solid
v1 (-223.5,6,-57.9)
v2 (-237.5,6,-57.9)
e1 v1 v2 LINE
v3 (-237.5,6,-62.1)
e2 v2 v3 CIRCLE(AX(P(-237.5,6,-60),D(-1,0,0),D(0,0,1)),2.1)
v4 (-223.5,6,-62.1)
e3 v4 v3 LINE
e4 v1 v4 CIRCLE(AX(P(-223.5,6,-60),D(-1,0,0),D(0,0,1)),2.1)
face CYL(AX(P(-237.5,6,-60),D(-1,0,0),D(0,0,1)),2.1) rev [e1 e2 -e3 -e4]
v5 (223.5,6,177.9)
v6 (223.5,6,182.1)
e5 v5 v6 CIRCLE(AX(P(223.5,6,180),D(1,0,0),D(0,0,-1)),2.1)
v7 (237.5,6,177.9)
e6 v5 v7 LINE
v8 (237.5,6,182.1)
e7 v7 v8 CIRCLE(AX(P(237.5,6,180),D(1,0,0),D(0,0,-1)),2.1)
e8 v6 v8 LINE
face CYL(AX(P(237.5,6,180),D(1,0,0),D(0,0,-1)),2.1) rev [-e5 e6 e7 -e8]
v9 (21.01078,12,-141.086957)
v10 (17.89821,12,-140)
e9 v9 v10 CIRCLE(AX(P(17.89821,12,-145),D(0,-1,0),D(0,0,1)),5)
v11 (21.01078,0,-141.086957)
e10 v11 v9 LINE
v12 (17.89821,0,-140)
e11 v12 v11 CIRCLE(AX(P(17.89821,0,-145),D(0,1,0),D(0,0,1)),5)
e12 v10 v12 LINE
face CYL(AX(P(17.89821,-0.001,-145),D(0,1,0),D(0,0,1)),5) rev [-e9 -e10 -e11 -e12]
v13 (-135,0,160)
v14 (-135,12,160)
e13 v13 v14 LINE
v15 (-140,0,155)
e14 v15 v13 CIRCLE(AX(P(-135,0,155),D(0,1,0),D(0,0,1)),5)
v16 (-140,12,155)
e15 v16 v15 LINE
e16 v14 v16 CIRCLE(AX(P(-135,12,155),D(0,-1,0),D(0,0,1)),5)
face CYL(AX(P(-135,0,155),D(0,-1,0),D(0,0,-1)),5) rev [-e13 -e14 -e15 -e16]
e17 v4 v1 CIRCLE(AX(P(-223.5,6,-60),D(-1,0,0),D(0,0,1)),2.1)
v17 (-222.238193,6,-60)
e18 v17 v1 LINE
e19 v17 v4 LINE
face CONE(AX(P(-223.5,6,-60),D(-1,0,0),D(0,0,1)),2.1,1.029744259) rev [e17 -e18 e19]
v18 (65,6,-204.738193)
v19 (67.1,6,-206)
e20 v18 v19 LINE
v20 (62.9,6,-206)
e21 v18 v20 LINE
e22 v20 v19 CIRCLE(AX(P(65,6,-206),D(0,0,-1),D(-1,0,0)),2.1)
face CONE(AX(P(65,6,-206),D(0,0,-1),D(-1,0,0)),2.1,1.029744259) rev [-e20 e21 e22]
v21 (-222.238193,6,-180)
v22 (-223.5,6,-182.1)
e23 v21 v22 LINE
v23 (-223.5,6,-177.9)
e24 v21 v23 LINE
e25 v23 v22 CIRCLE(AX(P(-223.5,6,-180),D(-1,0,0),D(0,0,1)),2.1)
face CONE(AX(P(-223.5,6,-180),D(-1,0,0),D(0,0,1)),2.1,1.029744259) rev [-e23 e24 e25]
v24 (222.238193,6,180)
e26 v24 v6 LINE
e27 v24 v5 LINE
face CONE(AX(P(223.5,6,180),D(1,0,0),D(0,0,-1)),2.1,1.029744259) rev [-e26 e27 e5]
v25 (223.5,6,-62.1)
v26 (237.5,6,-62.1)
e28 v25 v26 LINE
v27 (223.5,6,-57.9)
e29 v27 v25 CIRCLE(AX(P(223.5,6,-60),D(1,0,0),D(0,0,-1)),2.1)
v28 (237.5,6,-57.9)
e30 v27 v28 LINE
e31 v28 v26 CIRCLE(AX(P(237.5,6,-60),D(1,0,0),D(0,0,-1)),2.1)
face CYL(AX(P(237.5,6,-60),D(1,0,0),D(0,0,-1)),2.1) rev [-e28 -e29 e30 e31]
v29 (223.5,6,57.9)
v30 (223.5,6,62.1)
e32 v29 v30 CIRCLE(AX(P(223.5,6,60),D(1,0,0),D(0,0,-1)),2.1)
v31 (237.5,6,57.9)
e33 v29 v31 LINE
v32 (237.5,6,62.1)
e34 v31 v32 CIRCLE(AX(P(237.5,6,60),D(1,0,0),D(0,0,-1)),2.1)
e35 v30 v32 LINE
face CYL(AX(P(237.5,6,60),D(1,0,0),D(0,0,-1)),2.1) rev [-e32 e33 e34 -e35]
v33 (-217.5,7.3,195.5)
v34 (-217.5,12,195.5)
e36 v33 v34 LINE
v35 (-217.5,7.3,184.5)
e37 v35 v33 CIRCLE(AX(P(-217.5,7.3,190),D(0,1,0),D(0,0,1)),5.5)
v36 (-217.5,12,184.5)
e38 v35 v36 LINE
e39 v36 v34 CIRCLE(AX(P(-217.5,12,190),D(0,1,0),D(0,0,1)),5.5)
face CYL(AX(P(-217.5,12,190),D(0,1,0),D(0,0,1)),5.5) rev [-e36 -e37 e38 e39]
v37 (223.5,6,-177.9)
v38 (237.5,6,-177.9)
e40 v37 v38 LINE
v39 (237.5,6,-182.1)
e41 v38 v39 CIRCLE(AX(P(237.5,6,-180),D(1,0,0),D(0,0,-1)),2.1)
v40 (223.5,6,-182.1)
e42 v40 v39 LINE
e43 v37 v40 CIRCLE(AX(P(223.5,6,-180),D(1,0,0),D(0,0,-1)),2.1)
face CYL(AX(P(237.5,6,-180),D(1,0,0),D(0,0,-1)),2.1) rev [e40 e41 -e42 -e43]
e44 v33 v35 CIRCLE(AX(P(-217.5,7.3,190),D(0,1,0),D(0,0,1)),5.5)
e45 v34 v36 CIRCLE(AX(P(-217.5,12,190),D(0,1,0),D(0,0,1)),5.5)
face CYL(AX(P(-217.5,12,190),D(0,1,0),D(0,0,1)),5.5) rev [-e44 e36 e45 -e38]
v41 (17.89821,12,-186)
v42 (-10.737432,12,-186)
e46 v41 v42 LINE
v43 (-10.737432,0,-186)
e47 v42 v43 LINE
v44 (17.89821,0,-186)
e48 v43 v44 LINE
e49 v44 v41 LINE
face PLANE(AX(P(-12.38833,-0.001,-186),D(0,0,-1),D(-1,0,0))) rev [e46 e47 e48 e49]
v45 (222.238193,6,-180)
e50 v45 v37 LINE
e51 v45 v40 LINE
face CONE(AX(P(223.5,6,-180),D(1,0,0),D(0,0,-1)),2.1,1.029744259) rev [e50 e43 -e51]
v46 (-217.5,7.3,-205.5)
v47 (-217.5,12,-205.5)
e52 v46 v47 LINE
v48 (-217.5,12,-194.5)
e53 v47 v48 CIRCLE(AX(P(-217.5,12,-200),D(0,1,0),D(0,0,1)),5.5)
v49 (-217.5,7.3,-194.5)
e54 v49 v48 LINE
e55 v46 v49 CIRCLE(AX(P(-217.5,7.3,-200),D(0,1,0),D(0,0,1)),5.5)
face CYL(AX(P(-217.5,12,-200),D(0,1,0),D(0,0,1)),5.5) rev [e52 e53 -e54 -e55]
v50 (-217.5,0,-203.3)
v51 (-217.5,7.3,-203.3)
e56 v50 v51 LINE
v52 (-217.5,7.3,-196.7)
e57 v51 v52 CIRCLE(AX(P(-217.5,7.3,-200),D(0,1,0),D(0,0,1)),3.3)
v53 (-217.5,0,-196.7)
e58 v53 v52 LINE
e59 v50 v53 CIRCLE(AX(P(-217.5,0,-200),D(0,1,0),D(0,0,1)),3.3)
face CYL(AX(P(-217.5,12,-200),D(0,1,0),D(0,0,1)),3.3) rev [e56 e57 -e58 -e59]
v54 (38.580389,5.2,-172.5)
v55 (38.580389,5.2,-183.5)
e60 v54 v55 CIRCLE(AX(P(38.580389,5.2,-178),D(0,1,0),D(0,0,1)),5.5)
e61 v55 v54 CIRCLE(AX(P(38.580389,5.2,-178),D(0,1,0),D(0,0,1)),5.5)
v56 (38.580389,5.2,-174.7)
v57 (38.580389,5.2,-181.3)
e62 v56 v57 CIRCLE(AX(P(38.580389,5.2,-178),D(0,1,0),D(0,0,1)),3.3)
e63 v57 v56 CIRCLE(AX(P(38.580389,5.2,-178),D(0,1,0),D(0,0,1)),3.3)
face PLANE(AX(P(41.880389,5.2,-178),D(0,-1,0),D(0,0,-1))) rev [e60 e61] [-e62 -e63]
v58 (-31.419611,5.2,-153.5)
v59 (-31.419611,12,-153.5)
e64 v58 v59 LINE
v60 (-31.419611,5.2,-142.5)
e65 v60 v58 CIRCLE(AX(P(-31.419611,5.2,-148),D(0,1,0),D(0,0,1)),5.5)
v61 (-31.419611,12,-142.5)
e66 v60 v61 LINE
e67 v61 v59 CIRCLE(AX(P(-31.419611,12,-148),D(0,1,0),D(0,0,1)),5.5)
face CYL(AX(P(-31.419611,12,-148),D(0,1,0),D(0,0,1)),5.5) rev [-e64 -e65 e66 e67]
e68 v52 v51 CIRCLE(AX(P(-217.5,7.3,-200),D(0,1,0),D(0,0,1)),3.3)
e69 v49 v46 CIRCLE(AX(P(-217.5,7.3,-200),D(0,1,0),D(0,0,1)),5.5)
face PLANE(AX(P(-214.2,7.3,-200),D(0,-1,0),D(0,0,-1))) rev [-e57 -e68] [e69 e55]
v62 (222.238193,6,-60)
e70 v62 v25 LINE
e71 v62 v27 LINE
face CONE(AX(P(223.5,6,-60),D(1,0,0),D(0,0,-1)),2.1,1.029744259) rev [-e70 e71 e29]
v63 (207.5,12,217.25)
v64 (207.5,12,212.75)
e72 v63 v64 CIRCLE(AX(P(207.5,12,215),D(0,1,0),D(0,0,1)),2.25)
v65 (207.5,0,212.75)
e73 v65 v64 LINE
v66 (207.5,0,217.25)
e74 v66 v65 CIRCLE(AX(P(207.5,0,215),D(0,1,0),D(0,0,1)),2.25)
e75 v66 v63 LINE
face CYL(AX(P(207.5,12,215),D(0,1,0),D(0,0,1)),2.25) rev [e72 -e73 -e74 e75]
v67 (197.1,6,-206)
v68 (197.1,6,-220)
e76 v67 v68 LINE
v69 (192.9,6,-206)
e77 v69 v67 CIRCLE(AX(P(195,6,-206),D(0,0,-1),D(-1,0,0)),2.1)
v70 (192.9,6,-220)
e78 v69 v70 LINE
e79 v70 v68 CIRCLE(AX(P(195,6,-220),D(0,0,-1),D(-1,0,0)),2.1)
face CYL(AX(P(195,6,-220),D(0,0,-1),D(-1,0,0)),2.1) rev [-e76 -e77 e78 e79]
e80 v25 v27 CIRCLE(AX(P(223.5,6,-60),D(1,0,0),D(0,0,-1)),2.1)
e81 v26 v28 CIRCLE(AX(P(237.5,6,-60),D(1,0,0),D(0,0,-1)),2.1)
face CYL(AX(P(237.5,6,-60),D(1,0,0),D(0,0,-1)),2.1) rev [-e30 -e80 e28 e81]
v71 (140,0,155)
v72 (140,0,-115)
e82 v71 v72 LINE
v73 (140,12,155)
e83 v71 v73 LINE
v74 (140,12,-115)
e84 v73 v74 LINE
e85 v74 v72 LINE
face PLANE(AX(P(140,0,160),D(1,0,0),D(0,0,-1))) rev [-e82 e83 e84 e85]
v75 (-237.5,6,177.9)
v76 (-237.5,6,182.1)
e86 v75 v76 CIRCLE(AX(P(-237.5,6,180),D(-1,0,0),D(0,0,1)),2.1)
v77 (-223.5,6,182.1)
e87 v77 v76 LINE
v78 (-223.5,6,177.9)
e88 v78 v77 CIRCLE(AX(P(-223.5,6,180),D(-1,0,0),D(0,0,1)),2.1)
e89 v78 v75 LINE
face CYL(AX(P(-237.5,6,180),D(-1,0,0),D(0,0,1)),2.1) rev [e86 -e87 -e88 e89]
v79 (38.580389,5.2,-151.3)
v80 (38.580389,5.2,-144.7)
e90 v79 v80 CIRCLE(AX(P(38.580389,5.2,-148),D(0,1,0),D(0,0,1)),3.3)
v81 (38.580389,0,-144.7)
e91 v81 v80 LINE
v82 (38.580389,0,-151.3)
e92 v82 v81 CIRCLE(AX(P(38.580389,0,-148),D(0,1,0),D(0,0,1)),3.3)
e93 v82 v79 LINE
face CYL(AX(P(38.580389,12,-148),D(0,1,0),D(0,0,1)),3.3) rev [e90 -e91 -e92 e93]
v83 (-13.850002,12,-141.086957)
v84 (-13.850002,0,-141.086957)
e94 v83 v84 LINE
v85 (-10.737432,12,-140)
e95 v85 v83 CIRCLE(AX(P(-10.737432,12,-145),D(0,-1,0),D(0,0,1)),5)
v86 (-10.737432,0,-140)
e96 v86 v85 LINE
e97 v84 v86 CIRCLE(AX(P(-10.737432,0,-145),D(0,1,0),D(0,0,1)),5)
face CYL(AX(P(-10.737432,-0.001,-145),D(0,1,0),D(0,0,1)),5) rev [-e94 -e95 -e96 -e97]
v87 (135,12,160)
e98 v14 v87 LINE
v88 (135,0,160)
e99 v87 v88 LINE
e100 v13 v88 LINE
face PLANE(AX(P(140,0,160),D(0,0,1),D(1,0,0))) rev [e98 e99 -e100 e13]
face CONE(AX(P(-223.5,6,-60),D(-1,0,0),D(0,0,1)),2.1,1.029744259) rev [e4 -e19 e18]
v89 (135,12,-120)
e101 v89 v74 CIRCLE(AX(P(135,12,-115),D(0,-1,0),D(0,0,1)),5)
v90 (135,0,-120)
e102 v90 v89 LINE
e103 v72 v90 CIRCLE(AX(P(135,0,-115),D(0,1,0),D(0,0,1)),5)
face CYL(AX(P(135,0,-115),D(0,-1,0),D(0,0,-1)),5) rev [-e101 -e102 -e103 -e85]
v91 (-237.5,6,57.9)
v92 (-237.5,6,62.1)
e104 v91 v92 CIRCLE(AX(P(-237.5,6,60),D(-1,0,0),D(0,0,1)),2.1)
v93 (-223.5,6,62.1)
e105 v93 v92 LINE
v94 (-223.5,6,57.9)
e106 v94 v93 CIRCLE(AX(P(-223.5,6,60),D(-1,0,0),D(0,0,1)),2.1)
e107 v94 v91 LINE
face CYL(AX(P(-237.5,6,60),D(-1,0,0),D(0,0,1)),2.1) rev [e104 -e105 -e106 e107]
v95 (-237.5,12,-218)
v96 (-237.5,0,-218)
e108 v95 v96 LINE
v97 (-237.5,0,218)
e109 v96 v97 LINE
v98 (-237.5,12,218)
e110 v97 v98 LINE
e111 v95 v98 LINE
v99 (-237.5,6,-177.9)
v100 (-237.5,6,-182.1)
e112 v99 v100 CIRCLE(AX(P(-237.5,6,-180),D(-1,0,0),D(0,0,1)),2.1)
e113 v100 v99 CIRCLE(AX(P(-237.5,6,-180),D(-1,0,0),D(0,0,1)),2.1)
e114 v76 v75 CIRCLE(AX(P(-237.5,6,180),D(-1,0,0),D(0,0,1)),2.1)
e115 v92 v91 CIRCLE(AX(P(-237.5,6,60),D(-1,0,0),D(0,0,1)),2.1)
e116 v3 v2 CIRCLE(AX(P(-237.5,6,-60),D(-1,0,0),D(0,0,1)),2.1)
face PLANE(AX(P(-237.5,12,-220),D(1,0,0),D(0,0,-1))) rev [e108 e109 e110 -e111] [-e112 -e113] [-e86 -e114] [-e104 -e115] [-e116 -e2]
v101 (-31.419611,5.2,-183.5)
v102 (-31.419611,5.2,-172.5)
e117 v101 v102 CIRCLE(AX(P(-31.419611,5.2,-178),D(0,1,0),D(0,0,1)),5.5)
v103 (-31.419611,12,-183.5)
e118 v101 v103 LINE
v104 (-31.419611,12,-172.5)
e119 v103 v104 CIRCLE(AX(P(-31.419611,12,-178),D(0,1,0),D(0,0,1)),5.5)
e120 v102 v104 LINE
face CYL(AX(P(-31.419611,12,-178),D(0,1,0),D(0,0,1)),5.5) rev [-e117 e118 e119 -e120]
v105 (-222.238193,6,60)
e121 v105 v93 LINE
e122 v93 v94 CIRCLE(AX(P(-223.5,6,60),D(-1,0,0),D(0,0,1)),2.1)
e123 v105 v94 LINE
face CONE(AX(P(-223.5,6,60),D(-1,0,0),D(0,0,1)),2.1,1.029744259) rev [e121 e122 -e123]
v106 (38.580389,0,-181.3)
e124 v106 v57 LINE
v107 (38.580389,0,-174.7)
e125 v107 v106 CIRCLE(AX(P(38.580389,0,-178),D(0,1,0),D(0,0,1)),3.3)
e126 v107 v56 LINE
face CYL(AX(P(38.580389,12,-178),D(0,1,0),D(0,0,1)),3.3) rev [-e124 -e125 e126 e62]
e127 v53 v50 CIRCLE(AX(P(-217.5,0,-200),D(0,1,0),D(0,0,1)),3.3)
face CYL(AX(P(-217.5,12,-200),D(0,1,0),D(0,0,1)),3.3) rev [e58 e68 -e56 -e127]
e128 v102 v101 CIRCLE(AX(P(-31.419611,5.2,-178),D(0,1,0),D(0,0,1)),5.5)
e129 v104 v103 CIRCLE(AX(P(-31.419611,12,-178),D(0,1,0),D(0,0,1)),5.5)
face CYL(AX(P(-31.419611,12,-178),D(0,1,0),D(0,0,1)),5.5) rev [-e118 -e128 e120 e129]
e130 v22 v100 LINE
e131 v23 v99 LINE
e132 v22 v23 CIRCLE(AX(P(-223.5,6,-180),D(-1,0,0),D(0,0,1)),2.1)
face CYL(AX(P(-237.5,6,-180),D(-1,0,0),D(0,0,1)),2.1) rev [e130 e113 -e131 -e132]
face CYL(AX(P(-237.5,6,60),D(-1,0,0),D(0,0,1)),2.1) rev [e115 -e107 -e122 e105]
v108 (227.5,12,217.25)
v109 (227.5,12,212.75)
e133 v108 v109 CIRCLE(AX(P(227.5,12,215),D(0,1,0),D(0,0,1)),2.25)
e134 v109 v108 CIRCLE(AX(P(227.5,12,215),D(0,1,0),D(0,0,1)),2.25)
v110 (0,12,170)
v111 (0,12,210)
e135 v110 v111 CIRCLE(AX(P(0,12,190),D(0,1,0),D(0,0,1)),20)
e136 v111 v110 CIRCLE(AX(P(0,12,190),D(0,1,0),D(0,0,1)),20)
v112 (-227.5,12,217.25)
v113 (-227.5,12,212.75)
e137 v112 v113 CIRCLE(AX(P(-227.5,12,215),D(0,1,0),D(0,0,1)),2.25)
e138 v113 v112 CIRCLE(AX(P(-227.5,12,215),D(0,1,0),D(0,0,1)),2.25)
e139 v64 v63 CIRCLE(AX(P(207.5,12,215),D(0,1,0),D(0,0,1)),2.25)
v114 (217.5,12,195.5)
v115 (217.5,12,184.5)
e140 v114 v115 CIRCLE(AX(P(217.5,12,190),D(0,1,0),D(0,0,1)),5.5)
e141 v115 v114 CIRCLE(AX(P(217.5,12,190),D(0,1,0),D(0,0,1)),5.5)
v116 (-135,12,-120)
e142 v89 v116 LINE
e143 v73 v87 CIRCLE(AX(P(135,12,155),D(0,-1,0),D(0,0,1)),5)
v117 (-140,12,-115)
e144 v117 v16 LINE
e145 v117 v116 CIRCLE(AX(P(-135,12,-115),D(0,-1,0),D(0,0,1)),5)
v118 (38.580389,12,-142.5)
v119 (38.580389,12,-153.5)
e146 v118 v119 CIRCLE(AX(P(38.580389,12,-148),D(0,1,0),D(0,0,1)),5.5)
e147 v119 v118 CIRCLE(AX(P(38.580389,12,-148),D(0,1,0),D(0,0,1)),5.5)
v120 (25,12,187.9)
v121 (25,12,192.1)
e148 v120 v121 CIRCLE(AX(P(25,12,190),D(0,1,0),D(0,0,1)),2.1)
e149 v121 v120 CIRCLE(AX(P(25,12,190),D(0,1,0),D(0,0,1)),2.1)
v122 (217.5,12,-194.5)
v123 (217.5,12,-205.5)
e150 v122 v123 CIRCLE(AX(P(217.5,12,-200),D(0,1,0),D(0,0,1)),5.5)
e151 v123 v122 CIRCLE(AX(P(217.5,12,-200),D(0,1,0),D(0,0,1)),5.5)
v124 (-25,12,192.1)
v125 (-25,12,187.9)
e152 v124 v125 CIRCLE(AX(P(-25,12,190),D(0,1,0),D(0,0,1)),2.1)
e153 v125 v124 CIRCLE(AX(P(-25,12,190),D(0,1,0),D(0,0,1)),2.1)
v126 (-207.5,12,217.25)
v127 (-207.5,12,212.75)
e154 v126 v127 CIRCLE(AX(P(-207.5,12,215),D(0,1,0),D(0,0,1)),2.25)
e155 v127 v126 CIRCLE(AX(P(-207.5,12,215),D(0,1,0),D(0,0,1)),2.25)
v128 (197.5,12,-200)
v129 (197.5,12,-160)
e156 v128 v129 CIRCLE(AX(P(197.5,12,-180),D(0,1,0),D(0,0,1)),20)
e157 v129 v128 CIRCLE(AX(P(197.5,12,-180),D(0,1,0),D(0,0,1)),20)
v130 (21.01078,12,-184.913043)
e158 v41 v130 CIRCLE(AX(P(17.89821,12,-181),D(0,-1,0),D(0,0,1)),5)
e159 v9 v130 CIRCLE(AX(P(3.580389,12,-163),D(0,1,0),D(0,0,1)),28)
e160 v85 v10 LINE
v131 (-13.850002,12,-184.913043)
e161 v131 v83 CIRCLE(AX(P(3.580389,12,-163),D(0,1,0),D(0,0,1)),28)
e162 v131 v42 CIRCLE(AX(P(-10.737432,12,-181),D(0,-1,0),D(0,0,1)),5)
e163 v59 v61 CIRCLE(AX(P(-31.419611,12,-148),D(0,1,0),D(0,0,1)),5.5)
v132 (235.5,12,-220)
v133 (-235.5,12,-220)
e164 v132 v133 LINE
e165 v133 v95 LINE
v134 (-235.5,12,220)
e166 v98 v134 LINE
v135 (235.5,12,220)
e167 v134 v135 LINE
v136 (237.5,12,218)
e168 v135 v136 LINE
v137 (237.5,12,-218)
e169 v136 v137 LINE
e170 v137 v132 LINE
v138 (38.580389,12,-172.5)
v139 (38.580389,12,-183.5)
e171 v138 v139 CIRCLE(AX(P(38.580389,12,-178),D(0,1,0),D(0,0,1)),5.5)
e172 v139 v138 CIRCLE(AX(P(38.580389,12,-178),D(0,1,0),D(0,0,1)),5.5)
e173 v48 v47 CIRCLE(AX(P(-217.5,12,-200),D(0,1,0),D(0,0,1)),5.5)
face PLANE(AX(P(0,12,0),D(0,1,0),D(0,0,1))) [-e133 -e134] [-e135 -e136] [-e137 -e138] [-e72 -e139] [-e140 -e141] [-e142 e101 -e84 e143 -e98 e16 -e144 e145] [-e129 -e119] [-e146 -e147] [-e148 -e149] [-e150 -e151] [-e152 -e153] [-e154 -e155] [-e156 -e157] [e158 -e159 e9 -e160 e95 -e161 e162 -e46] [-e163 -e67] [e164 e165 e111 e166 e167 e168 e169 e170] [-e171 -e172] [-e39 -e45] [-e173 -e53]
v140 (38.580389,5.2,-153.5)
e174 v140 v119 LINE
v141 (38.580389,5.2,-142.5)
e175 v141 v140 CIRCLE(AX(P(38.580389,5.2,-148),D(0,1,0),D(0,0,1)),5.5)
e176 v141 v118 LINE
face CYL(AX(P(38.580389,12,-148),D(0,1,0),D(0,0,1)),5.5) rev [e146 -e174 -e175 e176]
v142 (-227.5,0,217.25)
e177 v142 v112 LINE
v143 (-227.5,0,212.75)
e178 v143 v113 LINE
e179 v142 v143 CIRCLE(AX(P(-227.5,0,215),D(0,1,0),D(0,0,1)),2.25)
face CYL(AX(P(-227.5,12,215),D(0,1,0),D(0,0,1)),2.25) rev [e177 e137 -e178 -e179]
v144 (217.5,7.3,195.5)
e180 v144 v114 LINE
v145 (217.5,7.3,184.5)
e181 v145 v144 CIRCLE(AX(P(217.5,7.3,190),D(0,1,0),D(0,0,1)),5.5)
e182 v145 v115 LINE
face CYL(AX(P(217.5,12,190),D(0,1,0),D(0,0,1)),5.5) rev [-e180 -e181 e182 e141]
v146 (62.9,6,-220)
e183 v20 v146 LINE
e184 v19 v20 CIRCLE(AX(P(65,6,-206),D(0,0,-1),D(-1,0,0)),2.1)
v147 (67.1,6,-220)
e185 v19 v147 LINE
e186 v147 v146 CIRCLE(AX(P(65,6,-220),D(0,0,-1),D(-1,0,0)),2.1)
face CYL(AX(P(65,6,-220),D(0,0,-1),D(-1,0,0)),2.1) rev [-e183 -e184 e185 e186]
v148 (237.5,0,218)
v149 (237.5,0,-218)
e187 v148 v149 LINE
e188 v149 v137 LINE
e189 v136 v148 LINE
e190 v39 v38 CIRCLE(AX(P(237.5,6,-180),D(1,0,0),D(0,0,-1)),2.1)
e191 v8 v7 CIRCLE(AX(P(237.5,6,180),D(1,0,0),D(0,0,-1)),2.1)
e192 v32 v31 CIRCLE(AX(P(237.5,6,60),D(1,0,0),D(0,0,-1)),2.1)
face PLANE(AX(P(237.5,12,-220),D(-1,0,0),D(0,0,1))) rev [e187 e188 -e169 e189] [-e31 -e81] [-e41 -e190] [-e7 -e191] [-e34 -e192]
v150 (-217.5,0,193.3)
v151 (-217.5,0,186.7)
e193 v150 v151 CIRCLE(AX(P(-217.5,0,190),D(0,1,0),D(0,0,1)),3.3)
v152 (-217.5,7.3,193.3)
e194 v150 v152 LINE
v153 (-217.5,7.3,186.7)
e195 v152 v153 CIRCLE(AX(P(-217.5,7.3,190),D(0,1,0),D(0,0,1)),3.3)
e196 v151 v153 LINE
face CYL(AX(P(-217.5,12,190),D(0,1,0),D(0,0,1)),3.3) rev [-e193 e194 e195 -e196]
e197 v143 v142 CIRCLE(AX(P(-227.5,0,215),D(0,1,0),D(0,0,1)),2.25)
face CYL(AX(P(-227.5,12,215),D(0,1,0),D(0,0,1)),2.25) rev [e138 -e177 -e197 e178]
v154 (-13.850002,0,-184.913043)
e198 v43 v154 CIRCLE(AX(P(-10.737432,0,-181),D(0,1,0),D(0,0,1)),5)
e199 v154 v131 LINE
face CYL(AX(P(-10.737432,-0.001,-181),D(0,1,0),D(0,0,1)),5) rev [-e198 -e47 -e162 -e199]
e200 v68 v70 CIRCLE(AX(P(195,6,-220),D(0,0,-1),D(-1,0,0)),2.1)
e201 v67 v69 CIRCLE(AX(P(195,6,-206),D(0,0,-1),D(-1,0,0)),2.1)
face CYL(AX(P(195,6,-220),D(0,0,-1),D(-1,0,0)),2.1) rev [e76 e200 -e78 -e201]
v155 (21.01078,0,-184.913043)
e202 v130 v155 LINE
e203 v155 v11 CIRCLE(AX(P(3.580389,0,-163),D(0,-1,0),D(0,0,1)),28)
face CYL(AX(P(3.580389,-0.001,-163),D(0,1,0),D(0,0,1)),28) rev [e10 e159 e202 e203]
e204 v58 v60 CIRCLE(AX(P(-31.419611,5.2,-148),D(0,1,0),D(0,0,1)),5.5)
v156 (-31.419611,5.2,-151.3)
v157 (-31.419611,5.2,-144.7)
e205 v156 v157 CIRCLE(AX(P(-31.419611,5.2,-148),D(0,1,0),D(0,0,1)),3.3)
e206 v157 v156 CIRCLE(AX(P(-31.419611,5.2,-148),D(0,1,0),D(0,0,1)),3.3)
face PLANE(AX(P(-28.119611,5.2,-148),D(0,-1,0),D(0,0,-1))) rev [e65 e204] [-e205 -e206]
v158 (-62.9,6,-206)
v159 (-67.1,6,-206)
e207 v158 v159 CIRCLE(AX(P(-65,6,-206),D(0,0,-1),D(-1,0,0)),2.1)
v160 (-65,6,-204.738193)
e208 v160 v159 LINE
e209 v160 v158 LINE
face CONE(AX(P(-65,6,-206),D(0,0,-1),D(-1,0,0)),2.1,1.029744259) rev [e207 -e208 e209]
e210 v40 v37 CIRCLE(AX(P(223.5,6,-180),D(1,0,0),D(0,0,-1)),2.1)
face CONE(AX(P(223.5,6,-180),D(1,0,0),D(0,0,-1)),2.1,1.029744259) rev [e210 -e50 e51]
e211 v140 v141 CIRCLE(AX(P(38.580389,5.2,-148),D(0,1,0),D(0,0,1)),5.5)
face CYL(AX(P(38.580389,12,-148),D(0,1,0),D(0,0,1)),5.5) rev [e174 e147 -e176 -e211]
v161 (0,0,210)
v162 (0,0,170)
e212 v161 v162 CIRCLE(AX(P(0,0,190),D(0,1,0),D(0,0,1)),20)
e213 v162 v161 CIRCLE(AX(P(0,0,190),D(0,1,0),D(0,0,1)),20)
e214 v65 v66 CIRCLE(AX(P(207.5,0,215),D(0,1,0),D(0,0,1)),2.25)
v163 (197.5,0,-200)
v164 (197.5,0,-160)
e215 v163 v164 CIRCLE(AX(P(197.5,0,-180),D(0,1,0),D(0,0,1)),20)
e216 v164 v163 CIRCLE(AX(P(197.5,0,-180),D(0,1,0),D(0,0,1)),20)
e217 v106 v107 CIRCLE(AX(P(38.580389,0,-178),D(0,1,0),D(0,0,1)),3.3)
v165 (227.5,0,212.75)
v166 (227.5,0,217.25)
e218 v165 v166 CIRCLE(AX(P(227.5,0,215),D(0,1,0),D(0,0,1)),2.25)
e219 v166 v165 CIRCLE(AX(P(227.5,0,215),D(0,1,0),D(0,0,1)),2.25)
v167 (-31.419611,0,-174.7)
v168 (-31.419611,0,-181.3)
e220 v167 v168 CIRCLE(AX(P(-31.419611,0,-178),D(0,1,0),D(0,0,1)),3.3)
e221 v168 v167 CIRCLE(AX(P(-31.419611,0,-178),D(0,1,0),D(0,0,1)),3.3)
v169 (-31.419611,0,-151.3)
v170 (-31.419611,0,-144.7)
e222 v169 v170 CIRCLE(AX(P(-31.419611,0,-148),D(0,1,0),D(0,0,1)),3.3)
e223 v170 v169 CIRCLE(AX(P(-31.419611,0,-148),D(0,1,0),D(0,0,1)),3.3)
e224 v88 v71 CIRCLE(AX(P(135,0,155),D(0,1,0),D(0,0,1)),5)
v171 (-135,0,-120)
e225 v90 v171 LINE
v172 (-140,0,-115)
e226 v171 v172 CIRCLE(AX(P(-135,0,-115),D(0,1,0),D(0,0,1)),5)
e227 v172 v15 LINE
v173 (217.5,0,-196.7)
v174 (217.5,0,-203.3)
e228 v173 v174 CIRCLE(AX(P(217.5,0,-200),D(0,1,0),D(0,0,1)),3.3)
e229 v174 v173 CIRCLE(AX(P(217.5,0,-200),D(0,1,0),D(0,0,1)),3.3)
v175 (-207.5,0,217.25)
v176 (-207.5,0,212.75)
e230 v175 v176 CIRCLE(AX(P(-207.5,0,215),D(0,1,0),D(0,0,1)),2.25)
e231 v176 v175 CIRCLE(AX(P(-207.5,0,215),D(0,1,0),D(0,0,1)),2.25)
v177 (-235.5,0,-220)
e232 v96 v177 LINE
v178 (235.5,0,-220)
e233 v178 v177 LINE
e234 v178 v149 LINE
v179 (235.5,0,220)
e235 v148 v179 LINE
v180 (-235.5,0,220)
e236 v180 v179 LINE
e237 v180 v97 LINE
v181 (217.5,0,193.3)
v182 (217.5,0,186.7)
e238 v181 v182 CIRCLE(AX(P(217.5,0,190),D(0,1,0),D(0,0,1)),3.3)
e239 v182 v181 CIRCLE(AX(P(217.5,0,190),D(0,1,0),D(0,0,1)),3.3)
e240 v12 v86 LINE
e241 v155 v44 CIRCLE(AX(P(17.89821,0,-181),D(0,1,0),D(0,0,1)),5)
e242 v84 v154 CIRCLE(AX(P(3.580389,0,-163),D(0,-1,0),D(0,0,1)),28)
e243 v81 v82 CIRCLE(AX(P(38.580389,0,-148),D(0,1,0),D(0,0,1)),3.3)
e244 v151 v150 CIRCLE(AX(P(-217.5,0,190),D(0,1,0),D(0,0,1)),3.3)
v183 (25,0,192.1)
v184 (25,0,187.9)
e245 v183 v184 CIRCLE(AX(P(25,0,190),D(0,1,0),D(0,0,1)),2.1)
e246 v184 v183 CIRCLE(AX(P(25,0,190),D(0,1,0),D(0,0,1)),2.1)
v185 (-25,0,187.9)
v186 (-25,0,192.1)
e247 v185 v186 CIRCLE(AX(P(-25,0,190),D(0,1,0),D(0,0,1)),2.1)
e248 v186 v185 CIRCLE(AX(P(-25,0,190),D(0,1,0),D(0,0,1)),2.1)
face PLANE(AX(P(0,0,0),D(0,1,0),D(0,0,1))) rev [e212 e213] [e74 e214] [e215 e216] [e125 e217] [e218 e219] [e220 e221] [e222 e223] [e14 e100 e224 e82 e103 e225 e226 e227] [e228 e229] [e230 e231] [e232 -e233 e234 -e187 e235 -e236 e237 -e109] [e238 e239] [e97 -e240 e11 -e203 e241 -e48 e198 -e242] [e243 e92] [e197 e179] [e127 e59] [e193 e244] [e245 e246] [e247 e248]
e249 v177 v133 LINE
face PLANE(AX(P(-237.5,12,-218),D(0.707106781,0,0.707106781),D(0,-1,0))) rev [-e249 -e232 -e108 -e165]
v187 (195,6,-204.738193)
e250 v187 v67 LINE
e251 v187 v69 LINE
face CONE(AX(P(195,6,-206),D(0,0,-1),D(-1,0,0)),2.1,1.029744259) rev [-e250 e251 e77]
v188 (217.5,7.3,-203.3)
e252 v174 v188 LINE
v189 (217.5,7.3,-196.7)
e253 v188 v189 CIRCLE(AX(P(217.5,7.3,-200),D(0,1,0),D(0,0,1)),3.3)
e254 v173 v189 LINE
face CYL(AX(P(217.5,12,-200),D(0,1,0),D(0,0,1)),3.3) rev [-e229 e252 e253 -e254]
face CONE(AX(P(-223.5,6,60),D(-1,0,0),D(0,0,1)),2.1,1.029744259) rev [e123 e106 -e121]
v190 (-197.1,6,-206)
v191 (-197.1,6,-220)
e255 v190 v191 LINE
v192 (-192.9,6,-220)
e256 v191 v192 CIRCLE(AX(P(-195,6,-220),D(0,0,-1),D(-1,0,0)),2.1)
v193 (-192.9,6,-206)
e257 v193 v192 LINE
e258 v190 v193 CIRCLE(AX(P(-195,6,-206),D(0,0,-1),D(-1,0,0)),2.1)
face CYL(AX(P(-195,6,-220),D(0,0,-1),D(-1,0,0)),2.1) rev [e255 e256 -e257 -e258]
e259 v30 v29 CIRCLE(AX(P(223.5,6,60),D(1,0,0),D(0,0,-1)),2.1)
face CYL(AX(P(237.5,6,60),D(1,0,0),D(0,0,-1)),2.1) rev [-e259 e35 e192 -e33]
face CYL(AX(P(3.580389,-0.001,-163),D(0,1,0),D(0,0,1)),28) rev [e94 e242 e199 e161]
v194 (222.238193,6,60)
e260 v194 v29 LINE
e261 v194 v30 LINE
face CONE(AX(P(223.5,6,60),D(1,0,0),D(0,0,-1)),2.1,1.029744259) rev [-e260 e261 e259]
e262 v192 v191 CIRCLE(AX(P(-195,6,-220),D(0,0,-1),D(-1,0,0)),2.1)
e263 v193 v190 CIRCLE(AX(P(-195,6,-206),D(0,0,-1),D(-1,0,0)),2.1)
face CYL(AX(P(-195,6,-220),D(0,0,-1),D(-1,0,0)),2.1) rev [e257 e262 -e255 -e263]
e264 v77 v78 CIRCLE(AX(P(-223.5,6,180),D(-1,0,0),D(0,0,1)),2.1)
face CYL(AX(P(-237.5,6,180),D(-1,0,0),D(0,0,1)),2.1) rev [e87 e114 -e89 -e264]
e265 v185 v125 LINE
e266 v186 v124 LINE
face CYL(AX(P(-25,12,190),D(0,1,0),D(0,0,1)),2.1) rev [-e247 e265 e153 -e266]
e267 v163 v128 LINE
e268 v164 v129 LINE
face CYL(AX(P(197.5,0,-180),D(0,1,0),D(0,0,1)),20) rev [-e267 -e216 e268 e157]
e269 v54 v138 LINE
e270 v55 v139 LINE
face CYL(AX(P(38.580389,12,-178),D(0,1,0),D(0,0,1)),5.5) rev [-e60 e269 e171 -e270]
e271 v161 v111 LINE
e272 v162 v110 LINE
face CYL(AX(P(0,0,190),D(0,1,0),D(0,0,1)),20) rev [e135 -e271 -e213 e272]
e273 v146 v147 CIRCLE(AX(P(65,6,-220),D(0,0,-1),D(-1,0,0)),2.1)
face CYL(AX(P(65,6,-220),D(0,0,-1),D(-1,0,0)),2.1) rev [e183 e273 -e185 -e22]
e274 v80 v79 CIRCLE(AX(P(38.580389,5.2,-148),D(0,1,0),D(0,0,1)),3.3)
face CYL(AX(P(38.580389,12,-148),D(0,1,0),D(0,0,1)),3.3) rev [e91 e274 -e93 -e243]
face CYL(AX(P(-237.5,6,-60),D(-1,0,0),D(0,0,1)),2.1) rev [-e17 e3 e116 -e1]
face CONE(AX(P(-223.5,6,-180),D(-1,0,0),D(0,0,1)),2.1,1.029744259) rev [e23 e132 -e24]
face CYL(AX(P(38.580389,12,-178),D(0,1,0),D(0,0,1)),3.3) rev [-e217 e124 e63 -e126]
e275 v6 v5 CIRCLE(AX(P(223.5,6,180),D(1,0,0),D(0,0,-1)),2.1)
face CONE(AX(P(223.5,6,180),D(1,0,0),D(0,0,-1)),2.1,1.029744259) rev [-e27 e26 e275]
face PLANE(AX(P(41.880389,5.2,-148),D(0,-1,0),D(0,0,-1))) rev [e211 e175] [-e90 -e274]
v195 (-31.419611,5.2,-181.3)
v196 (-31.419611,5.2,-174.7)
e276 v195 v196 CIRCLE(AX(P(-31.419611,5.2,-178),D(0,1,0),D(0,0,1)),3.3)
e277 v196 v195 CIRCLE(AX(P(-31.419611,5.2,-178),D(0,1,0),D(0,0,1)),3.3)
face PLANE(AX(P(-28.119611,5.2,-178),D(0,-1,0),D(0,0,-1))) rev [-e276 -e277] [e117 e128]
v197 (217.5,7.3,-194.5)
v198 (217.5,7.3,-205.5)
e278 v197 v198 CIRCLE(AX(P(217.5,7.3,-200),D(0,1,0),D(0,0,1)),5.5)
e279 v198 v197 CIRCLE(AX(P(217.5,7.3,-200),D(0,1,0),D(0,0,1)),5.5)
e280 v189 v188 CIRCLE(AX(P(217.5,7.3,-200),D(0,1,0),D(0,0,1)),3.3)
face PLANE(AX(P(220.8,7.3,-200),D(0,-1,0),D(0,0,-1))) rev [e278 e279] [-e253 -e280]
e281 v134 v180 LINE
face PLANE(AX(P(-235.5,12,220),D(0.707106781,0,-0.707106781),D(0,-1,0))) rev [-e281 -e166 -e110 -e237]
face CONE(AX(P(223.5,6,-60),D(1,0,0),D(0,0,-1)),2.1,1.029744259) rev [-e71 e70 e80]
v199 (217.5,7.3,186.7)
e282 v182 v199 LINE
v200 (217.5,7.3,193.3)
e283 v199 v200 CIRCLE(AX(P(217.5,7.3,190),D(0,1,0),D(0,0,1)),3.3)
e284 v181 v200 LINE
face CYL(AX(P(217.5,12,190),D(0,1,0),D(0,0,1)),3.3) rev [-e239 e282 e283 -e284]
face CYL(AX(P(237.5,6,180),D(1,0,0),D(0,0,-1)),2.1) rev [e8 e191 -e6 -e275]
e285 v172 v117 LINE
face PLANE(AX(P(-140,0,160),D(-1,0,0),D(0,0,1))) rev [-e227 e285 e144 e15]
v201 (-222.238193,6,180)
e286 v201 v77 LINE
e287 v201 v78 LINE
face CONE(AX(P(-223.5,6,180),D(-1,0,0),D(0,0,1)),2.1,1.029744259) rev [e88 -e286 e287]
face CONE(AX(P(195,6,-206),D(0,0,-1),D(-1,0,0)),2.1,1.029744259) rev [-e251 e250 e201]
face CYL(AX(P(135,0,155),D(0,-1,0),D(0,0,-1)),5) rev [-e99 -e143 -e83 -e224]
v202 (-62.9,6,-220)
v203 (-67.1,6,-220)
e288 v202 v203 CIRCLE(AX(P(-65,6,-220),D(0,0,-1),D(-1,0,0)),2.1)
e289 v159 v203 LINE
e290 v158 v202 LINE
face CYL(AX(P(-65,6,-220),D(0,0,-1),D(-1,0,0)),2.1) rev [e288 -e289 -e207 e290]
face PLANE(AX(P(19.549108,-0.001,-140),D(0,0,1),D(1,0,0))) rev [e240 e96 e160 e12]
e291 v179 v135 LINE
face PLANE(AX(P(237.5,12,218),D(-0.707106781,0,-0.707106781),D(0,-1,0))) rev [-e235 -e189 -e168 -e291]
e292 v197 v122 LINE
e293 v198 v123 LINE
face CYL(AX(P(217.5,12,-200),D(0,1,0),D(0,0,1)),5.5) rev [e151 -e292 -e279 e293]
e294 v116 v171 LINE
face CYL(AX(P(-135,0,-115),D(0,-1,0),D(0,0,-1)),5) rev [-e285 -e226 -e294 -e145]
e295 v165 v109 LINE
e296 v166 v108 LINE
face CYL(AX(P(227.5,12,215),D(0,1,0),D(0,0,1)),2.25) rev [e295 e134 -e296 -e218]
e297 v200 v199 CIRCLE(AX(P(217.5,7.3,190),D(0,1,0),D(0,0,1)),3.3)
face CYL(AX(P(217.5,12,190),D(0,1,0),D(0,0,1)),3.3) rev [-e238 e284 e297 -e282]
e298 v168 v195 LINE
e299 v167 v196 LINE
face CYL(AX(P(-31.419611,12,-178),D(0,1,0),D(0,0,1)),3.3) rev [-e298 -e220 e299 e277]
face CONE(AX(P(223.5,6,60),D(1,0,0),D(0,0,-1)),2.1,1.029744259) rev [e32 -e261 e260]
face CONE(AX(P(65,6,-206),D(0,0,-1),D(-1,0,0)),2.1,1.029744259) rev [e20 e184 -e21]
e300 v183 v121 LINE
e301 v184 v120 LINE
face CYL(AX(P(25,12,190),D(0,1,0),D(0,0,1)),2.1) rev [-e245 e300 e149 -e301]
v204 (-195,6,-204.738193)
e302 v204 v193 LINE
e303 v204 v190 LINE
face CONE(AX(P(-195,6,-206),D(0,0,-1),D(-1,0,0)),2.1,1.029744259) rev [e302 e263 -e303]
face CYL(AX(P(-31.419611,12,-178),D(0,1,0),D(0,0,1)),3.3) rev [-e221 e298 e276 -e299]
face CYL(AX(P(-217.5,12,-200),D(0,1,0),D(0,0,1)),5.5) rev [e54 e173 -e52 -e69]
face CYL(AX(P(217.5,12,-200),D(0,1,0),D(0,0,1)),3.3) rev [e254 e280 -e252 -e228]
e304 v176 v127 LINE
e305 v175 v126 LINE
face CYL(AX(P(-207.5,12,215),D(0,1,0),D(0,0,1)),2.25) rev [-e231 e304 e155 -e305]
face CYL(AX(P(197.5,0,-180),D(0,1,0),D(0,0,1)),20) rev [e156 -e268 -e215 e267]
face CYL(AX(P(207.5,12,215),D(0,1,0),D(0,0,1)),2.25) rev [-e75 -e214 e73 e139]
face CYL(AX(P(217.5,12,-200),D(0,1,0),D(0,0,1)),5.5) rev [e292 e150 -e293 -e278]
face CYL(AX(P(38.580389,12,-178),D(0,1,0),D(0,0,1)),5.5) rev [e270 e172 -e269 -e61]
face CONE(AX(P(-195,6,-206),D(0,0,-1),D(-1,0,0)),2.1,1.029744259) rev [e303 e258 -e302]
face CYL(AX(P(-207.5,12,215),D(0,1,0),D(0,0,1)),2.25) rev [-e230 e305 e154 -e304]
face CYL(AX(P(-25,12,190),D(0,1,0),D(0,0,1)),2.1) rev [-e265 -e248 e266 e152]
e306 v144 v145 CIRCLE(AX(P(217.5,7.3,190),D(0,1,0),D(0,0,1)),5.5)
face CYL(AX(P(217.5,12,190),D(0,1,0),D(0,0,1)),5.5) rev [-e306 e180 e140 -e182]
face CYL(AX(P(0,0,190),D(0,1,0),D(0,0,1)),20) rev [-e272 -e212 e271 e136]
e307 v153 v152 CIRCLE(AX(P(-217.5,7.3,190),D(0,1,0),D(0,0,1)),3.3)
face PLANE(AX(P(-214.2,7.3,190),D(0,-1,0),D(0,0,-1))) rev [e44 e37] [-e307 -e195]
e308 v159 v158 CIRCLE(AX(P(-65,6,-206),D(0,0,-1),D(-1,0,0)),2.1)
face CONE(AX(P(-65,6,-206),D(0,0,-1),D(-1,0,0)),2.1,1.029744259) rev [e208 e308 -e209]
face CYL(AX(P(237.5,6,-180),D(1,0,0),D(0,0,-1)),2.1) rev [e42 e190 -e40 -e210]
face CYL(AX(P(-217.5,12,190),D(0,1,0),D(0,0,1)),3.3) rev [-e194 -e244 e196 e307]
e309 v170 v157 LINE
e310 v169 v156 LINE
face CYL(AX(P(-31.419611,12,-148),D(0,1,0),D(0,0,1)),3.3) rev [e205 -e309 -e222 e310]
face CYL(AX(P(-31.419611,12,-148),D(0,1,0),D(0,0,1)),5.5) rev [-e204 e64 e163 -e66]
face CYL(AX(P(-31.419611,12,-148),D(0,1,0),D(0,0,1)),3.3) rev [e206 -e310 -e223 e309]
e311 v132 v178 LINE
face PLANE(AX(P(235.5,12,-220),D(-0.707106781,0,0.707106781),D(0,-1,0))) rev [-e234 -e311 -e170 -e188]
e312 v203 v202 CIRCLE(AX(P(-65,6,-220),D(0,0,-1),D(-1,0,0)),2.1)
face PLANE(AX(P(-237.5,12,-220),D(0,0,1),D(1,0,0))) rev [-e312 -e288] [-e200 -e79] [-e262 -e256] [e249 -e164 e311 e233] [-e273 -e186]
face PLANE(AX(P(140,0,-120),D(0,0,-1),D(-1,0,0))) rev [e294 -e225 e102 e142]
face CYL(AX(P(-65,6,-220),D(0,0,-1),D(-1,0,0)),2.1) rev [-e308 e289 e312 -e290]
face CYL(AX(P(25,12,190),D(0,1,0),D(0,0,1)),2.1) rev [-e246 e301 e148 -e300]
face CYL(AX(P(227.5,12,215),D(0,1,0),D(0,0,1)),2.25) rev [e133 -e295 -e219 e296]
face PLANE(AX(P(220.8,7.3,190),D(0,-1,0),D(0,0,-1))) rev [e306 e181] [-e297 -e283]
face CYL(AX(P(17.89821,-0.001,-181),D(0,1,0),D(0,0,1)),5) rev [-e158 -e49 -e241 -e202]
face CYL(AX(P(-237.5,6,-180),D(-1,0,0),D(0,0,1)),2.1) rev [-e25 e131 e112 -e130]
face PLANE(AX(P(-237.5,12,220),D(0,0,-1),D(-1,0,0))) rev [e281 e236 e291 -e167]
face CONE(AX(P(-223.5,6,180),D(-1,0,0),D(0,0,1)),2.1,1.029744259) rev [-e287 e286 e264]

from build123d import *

# Parameters (mm, degrees)
SKETCH1_W                                       = 475
SKETCH1_H                                       = 440
BOSS_EXTRUDE1_DEPTH                             = 12
SKETCH3_R                                       = 20
CUT_EXTRUDE2_DEPTH                              = 324.960259909
HEX_SOCKET_BUTTON_HEAD_SCREW_HOLE_1_D           = 6.6
HEX_SOCKET_BUTTON_HEAD_SCREW_HOLE_1_CBORE_D     = 11
HEX_SOCKET_BUTTON_HEAD_SCREW_HOLE_1_CBORE_DEPTH = 4.7
CHAMFER1_SIZE                                   = 2
CUT_EXTRUDE4_REACH                              = 325.96
HEX_SOCKET_CAP_SCREW_HOLE_TYPE_1_D              = 6.6
HEX_SOCKET_CAP_SCREW_HOLE_TYPE_1_CBORE_D        = 11
HEX_SOCKET_CAP_SCREW_HOLE_TYPE_1_CBORE_DEPTH    = 6.8
FILLET1_R                                       = 5
M5_TAPPED_HOLE1_D                               = 4.2
M5_TAPPED_HOLE2_AT_2_COUNT                      = 2
M5_TAPPED_HOLE2_AT_2_PITCH                      = 120
M5_TAPPED_HOLE2_AT_3_COUNT                      = 2
M5_TAPPED_HOLE2_AT_3_PITCH                      = 240
M5_TAPPED_HOLE2_AT_4_COUNT                      = 2
M5_TAPPED_HOLE2_AT_4_PITCH                      = 360
M5_TAPPED_HOLE3_D                               = 4.2
M5_TAPPED_HOLE3_DEPTH                           = 14
M5_TAPPED_HOLE3_TIP                             = 1.2618073
M4_CLEARANCE_HOLE1_D                            = 4.5
SKETCH46_W                                      = 280
SKETCH46_H                                      = 280
CUT_EXTRUDE5_DEPTH                              = 324.960259909
FILLET2_R                                       = 5
SKETCH47_R                                      = 20
CUT_EXTRUDE6_DEPTH                              = 324.960259909


with BuildPart() as part:
    # Sketch1 → Boss-Extrude1 (new body)
    with BuildSketch(Plane(origin=(0, 0, 0), x_dir=(1, 0, 0), z_dir=(0, 1, 0))):
        Rectangle(SKETCH1_W, SKETCH1_H)
    extrude(amount=BOSS_EXTRUDE1_DEPTH)

    # Sketch3 → Cut-Extrude2 (cut, through all)
    with BuildSketch(Plane(origin=(0, 12, 0), x_dir=(1, 0, 0), z_dir=(0, 1, 0))):
        with Locations(Location((0, -190, 0), (0, 0, 270))):
            Circle(SKETCH3_R)
    extrude(amount=-CUT_EXTRUDE2_DEPTH, mode=Mode.SUBTRACT)

    # Hex socket button head screw hole 1 (through all)
    with Locations(Plane(origin=(0, 12, 0), x_dir=(1, 0, 0), z_dir=(0, 1, 0))):
        with Locations((217.5, 200), (217.5, -190), (-217.5, -190), (-217.5, 200)):
            CounterBoreHole(HEX_SOCKET_BUTTON_HEAD_SCREW_HOLE_1_D / 2, HEX_SOCKET_BUTTON_HEAD_SCREW_HOLE_1_CBORE_D / 2, HEX_SOCKET_BUTTON_HEAD_SCREW_HOLE_1_CBORE_DEPTH)

    # Chamfer1
    chamfer1_edges = [part.edges().sort_by_distance(p)[0] for p in [
        (237.5, 6, 220),
        (-237.5, 6, 220),
        (-237.5, 6, -220),
        (237.5, 6, -220),
    ]]
    chamfer(chamfer1_edges, length=CHAMFER1_SIZE)

    # Sketch33 → Cut-Extrude4 (cut, up to next)
    with BuildSketch(Plane(origin=(0, 12, 0), x_dir=(1, 0, 0), z_dir=(0, 1, 0)), mode=Mode.PRIVATE) as cut_extrude4_sk1:
        with BuildLine():
            Line((-12.388330441, 186), (19.549108404, 186))
            ThreePointArc((19.549108404, 186), (31.580388981, 163), (19.549108404, 140))
            Line((19.549108404, 140), (-12.388330441, 140))
            ThreePointArc((-12.388330441, 140), (-24.419611019, 163), (-12.388330441, 186))
        make_face()
    cut_extrude4_tool1 = extrude(cut_extrude4_sk1.sketch, amount=-CUT_EXTRUDE4_REACH, mode=Mode.PRIVATE) & part.part
    add(cut_extrude4_tool1.solids().sort_by_distance((3.580389, 12, -163))[0], mode=Mode.SUBTRACT)

    # Hex socket cap screw hole type 1 (through all)
    with Locations(Plane(origin=(0, 12, 0), x_dir=(1, 0, 0), z_dir=(0, 1, 0))):
        with Locations((38.580388981, 148), (38.580388981, 178), (-31.419611019, 148), (-31.419611019, 178)):
            CounterBoreHole(HEX_SOCKET_CAP_SCREW_HOLE_TYPE_1_D / 2, HEX_SOCKET_CAP_SCREW_HOLE_TYPE_1_CBORE_D / 2, HEX_SOCKET_CAP_SCREW_HOLE_TYPE_1_CBORE_DEPTH)

    # Fillet1
    fillet1_edges = [part.edges().sort_by_distance(p)[0] for p in [
        (19.549108404, 6, -186),
        (19.549108404, 6, -140),
        (-12.388330441, 6, -140),
        (-12.388330441, 6, -186),
    ]]
    fillet(fillet1_edges, radius=FILLET1_R)

    # M5 Tapped Hole1 (through all)
    with Locations(Plane(origin=(0, 12, 0), x_dir=(1, 0, 0), z_dir=(0, 1, 0))):
        with Locations((-25, -190), (25, -190)):
            Hole(M5_TAPPED_HOLE1_D / 2)

    # Sketch39 → M5 Tapped Hole2 (revolve, cut)
    with BuildSketch(Plane(origin=(-237.5, 6, -180), x_dir=(0, 0, 1), z_dir=(0, 1, 0))):
        Polygon((0, 0), (0, 15.2618073), (2.1, 14), (2.1, 0), align=None)
    m5_tapped_hole2 = revolve(axis=Axis((-243.85, 6, -180), (1, 0, 0)), mode=Mode.SUBTRACT)

    # M5 Tapped Hole2 at 2: M5 Tapped Hole2 ×2
    with Locations(*[(0, 0, i * M5_TAPPED_HOLE2_AT_2_PITCH) for i in range(1, M5_TAPPED_HOLE2_AT_2_COUNT)]):
        add(m5_tapped_hole2, mode=Mode.SUBTRACT)

    # M5 Tapped Hole2 at 3: M5 Tapped Hole2 ×2
    with Locations(*[(0, 0, i * M5_TAPPED_HOLE2_AT_3_PITCH) for i in range(1, M5_TAPPED_HOLE2_AT_3_COUNT)]):
        add(m5_tapped_hole2, mode=Mode.SUBTRACT)

    # M5 Tapped Hole2 at 4: M5 Tapped Hole2 ×2
    with Locations(*[(0, 0, i * M5_TAPPED_HOLE2_AT_4_PITCH) for i in range(1, M5_TAPPED_HOLE2_AT_4_COUNT)]):
        add(m5_tapped_hole2, mode=Mode.SUBTRACT)

    # Mirror1: M5 Tapped Hole2 across plane
    add(m5_tapped_hole2.mirror(Plane(origin=(0, 0, 0), x_dir=(0, 0, 1), z_dir=(1, 0, 0))), mode=Mode.SUBTRACT)

    # Mirror1 copy 1 sketch → Mirror1 copy 1 (revolve, cut)
    with BuildSketch(Plane(origin=(237.5, 6, -60), x_dir=(0, 0, 1), z_dir=(0, 1, 0))):
        Polygon((0, 0), (0, -15.2618073), (2.1, -14), (2.1, 0), align=None)
    revolve(axis=Axis((243.85, 6, -60), (1, 0, 0)), mode=Mode.SUBTRACT)

    # Mirror1 copy 2 sketch → Mirror1 copy 2 (revolve, cut)
    with BuildSketch(Plane(origin=(237.5, 6, 60), x_dir=(0, 0, 1), z_dir=(0, 1, 0))):
        Polygon((0, 0), (0, -15.2618073), (2.1, -14), (2.1, 0), align=None)
    revolve(axis=Axis((243.85, 6, 60), (1, 0, 0)), mode=Mode.SUBTRACT)

    # Mirror1 copy 3 sketch → Mirror1 copy 3 (revolve, cut)
    with BuildSketch(Plane(origin=(237.5, 6, 180), x_dir=(0, 0, 1), z_dir=(0, 1, 0))):
        Polygon((0, 0), (0, -15.2618073), (2.1, -14), (2.1, 0), align=None)
    revolve(axis=Axis((243.85, 6, 180), (1, 0, 0)), mode=Mode.SUBTRACT)

    # M5 Tapped Hole3
    with Locations(Plane(origin=(0, 0, -220), x_dir=(-1, 0, 0), z_dir=(0, 0, -1))):
        with Locations((-195, 6), (-65, 6), (65, 6), (195, 6)):
            Hole(M5_TAPPED_HOLE3_D / 2, depth=M5_TAPPED_HOLE3_DEPTH)
            with Locations((0, 0, -(M5_TAPPED_HOLE3_DEPTH + M5_TAPPED_HOLE3_TIP / 2))):  # 118° drill point
                Cone(0, M5_TAPPED_HOLE3_D / 2, M5_TAPPED_HOLE3_TIP, mode=Mode.SUBTRACT)

    # M4 Clearance Hole1 (through all)
    with Locations(Plane(origin=(0, 12, 0), x_dir=(1, 0, 0), z_dir=(0, 1, 0))):
        with Locations((-227.5, -215), (-207.5, -215), (207.5, -215), (227.5, -215)):
            Hole(M4_CLEARANCE_HOLE1_D / 2)

    # Sketch46 → Cut-Extrude5 (cut, through all)
    with BuildSketch(Plane(origin=(0, 12, 0), x_dir=(1, 0, 0), z_dir=(0, 1, 0))):
        with Locations((0, -20)):
            Rectangle(SKETCH46_W, SKETCH46_H)
    extrude(amount=-CUT_EXTRUDE5_DEPTH, mode=Mode.SUBTRACT)

    # Fillet2
    fillet2_edges = [part.edges().sort_by_distance(p)[0] for p in [
        (-140, 6, 160),
        (-140, 6, -120),
        (140, 6, -120),
        (140, 6, 160),
    ]]
    fillet(fillet2_edges, radius=FILLET2_R)

    # Sketch47 → Cut-Extrude6 (cut, through all)
    with BuildSketch(Plane(origin=(0, 12, 0), x_dir=(1, 0, 0), z_dir=(0, 1, 0))):
        with Locations(Location((197.5, 180, 0), (0, 0, 270))):
            Circle(SKETCH47_R)
    extrude(amount=-CUT_EXTRUDE6_DEPTH, mode=Mode.SUBTRACT)


solid = part.part
